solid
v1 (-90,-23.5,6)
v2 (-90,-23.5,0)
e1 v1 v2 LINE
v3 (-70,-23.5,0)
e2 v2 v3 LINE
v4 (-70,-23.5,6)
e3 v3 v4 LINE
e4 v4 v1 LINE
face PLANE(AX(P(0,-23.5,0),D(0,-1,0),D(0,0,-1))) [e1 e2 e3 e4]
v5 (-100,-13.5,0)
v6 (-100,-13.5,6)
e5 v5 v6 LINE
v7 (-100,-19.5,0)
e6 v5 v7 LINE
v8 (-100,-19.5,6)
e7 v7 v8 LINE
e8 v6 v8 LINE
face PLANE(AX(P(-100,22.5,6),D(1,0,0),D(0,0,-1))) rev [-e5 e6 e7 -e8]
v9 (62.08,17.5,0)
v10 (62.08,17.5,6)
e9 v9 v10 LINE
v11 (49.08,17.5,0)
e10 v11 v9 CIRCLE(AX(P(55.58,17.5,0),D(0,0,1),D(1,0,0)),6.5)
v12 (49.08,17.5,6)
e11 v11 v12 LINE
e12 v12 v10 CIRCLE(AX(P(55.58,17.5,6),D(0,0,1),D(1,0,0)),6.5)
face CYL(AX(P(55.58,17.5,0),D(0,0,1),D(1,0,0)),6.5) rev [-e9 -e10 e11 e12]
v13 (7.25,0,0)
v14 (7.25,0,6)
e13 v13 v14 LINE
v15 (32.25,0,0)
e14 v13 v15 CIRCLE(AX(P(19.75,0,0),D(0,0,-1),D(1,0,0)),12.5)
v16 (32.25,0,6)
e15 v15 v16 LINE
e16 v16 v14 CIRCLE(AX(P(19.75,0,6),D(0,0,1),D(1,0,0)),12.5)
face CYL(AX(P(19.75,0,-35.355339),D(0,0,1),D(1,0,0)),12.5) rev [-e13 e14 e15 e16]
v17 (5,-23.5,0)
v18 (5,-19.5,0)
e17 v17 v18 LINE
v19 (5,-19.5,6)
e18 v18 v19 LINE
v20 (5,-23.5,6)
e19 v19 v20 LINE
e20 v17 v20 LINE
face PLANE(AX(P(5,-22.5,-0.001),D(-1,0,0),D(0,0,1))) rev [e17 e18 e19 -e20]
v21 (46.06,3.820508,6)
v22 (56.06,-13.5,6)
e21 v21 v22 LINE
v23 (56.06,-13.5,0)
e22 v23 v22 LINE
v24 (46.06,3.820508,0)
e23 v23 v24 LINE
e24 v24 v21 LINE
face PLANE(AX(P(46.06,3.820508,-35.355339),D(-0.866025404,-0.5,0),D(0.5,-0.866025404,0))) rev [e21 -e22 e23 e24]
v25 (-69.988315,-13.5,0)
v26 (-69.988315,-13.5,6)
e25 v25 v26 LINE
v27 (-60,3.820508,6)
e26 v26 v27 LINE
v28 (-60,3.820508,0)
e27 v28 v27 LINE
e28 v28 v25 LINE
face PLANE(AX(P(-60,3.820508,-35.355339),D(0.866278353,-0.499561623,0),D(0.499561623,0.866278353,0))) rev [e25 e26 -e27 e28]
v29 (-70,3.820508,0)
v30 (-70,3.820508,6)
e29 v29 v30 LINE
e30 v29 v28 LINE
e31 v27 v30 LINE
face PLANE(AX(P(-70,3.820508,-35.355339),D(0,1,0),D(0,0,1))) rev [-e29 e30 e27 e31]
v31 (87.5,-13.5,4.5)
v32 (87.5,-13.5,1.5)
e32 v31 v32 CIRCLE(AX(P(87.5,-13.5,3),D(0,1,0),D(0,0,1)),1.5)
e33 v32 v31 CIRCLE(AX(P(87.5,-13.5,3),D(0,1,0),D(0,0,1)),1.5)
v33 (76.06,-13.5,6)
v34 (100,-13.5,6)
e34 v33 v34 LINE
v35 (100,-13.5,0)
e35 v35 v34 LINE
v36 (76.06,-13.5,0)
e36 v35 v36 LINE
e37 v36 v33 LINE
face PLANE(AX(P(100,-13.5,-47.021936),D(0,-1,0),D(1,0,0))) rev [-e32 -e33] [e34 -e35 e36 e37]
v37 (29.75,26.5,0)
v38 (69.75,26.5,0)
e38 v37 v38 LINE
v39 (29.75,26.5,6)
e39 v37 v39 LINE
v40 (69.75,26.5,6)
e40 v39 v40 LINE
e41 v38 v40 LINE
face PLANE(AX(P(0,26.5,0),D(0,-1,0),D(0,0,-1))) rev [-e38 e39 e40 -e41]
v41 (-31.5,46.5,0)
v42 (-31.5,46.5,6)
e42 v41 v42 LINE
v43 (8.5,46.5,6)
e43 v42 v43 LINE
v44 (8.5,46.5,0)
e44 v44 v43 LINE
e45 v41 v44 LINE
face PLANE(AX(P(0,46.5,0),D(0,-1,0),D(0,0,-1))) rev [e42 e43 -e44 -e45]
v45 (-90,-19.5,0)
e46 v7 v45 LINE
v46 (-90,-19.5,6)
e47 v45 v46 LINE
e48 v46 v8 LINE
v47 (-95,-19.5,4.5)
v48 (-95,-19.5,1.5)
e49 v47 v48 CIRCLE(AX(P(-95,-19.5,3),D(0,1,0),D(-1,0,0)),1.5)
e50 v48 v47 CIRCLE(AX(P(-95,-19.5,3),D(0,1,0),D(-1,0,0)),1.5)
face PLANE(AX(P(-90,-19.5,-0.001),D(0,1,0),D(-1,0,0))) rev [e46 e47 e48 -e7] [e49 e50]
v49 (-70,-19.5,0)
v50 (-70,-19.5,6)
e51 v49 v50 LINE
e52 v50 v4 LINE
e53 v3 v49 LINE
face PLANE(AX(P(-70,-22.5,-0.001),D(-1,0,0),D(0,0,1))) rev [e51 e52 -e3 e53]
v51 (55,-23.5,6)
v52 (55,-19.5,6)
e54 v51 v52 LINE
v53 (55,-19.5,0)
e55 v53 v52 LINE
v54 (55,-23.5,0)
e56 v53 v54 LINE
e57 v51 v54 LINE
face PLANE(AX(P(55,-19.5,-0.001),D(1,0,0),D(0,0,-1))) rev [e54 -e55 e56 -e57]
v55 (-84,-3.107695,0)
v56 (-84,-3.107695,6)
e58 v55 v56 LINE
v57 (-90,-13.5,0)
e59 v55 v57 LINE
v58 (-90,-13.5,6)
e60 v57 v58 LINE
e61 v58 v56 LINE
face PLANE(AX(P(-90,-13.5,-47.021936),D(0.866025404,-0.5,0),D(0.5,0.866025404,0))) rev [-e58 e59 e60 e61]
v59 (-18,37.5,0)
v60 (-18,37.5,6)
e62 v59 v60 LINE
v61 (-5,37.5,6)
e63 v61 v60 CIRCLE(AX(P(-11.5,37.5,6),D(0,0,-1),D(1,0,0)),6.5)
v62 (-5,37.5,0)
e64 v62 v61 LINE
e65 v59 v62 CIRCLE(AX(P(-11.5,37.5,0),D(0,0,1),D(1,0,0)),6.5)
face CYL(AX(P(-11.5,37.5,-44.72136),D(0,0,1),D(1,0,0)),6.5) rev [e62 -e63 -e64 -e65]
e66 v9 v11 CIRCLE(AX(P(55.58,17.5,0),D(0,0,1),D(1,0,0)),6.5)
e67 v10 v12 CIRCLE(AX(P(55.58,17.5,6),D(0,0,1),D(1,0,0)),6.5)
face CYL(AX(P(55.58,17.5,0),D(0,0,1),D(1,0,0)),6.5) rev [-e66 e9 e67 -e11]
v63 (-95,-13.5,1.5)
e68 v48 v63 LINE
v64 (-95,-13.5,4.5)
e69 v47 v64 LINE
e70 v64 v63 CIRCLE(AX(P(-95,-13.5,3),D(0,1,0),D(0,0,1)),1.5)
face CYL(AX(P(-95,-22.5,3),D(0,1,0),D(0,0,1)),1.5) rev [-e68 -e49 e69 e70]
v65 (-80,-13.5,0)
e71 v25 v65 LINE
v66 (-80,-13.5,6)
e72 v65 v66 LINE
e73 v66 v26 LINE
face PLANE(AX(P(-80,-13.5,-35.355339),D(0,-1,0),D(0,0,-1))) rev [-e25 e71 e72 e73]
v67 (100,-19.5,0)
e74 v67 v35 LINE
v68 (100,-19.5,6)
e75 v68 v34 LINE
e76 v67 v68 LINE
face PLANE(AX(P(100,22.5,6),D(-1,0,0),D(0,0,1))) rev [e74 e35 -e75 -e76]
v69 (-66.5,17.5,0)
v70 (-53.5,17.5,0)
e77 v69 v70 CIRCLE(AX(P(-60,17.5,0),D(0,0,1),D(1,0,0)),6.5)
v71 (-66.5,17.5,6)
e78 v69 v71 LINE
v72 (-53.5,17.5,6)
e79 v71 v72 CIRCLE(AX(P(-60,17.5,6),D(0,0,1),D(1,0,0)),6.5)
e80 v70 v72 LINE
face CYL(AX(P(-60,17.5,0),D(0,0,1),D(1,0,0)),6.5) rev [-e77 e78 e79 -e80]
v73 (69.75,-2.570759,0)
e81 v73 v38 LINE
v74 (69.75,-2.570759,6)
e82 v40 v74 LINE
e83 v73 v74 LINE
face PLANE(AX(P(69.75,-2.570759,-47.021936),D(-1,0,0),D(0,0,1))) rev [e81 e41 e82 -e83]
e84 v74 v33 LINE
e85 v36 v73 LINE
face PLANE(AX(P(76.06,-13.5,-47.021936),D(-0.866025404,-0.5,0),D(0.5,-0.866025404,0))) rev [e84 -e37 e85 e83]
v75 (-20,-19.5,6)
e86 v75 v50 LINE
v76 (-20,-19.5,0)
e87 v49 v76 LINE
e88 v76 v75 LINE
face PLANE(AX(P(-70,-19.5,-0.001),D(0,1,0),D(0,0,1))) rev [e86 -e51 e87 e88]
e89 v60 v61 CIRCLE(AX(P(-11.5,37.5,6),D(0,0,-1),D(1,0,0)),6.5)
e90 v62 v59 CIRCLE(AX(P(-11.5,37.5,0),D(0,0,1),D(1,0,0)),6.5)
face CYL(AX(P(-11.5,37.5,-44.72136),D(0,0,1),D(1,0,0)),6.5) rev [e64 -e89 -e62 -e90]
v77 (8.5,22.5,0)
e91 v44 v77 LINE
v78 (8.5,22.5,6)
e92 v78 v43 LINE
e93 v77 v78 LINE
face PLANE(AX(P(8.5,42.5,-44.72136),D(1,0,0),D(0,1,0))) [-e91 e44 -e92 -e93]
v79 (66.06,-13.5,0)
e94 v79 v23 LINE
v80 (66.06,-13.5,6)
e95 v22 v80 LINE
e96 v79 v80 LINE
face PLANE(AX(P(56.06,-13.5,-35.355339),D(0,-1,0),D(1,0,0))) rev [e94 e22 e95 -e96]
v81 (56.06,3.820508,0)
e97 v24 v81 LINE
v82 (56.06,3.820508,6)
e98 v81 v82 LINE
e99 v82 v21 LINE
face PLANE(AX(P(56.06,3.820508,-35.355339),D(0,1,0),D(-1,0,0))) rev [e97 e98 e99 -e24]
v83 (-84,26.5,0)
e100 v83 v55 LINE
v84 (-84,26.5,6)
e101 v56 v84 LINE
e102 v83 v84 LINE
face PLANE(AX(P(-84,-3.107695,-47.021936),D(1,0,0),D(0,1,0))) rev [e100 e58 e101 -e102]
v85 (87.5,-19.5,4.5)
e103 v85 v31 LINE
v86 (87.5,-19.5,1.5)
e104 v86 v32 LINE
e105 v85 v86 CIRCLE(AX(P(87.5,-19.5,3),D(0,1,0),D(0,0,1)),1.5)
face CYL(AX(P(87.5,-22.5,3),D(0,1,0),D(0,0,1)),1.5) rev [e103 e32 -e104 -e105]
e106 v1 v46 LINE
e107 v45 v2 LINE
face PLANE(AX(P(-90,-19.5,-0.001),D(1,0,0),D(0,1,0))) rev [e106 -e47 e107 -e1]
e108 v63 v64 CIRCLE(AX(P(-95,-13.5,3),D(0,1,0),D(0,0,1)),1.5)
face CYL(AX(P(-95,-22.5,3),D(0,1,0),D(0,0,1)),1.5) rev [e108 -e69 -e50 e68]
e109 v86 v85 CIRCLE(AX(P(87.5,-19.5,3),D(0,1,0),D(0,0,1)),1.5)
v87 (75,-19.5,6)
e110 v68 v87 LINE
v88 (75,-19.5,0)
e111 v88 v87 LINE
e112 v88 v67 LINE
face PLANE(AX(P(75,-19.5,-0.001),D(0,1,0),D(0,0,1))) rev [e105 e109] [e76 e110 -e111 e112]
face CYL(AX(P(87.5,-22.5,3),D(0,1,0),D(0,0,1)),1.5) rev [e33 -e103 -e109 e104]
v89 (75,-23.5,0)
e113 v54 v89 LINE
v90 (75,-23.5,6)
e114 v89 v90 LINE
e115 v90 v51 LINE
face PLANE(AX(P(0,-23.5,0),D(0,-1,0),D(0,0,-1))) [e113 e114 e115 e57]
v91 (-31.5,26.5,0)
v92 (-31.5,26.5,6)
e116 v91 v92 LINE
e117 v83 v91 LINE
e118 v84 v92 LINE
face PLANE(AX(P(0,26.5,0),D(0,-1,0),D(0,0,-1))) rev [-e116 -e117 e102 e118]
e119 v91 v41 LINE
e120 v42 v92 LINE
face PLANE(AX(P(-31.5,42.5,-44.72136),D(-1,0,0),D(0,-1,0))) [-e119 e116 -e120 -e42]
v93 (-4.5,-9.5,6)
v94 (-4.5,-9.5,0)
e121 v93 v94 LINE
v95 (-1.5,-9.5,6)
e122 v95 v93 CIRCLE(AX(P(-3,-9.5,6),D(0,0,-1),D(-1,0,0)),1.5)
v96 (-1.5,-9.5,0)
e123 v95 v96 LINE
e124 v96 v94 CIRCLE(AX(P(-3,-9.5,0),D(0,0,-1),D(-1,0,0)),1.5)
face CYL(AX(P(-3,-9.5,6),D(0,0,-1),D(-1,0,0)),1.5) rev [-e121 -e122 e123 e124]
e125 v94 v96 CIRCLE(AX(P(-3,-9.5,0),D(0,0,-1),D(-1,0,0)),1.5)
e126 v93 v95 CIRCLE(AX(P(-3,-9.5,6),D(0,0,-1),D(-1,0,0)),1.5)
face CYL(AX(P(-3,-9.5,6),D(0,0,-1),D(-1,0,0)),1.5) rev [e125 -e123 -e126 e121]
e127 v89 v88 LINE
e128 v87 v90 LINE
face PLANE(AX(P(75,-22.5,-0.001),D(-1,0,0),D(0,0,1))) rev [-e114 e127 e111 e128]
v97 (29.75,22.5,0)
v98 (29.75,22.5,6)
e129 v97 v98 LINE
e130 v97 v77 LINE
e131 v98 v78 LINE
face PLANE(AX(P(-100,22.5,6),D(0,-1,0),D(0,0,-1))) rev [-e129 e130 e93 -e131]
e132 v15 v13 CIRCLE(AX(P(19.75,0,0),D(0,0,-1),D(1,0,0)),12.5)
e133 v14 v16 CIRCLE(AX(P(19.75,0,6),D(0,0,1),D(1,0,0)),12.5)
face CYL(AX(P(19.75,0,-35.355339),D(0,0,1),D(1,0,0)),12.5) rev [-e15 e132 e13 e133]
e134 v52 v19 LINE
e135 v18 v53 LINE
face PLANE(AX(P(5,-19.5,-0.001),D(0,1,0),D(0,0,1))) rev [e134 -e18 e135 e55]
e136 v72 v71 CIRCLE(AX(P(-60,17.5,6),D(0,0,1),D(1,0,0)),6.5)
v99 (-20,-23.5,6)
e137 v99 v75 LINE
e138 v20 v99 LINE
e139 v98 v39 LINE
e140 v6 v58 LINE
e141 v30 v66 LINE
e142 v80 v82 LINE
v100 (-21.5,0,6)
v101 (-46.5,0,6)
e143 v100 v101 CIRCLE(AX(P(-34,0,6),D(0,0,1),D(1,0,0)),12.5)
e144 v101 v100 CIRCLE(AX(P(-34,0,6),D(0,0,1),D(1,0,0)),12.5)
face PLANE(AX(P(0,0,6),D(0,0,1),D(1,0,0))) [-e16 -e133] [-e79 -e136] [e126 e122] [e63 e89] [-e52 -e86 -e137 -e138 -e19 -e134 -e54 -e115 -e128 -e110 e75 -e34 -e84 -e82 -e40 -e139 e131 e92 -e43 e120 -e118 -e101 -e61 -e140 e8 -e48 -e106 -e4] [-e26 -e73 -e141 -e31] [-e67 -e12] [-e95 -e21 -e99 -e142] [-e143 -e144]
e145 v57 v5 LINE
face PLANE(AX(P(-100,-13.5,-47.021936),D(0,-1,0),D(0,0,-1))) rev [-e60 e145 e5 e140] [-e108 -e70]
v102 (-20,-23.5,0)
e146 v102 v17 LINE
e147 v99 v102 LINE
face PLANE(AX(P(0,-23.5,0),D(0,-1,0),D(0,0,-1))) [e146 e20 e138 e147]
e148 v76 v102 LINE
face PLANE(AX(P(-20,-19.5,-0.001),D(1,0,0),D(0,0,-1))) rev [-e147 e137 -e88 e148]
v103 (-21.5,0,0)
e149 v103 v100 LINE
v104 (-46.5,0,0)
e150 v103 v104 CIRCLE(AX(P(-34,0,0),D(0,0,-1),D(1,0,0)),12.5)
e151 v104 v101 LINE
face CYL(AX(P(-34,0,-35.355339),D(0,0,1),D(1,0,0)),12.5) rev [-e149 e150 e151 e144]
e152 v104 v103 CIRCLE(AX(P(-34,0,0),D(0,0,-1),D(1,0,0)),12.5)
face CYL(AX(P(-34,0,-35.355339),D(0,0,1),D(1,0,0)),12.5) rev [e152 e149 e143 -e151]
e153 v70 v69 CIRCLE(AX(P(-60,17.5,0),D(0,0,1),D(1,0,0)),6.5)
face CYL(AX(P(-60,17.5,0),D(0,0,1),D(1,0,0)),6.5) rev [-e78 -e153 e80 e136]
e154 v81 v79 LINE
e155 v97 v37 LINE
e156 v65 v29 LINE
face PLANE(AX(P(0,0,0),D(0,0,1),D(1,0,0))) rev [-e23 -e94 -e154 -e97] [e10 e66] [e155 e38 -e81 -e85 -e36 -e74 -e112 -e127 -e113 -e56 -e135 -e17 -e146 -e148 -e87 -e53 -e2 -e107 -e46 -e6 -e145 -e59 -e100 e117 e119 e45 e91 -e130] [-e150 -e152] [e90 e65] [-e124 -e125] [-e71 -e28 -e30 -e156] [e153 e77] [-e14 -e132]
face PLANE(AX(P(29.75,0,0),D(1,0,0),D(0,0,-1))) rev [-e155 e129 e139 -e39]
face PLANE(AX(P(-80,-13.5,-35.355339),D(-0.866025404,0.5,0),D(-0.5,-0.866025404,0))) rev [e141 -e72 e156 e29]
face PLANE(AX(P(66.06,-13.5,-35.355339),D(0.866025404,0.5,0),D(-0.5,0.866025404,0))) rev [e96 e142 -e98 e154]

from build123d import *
from build123d.topology import SkipClean

# Parameters (mm, degrees)
SKETCH1_W           = 200
SKETCH1_H           = 45
BOSS_EXTRUDE1_DEPTH = 6
CUT_EXTRUDE1_REACH  = 104.675
SKETCH2_W           = 10
SKETCH2_H           = 3
SKETCH2_W_2         = 50
SKETCH2_W_3         = 25
BOSS_EXTRUDE2_DEPTH = 6
CUT_EXTRUDE2_DEPTH  = 6
CUT_EXTRUDE3_DEPTH  = 6
SKETCH15_R          = 12.5
CUT_EXTRUDE4_DEPTH  = 6
BOSS_EXTRUDE3_DEPTH = 6
SKETCH20_R          = 1.5
CUT_EXTRUDE5_DEPTH  = 111.44568801
SKETCH21_R          = 1.5
CUT_EXTRUDE6_DEPTH  = 117.773284616
SKETCH24_W          = 20
SKETCH24_H          = 6
SKETCH24_W_2        = 25
BOSS_EXTRUDE4_DEPTH = 1
SKETCH25_R          = 6.5
BOSS_EXTRUDE5_DEPTH = 6
SKETCH26_R          = 6.5
CUT_EXTRUDE7_DEPTH  = 111.44568801


with BuildPart() as part:
    # Sketch1 → Boss-Extrude1 (new body)
    with BuildSketch(Plane.XY):
        Rectangle(SKETCH1_W, SKETCH1_H)
    extrude(amount=BOSS_EXTRUDE1_DEPTH)

    # Sketch2 → Cut-Extrude1 (cut, up to next)
    with BuildSketch(Plane.XY.offset(6), mode=Mode.PRIVATE) as cut_extrude1_sk1:
        with Locations((-95, -21)):
            Rectangle(SKETCH2_W, SKETCH2_H)
    cut_extrude1_tool1 = extrude(cut_extrude1_sk1.sketch, amount=-CUT_EXTRUDE1_REACH, mode=Mode.PRIVATE) & part.part
    # Sketch2 → Cut-Extrude1 (cut, up to next)
    with BuildSketch(Plane.XY.offset(6), mode=Mode.PRIVATE) as cut_extrude1_sk2:
        with Locations((-45, -21)):
            Rectangle(SKETCH2_W_2, SKETCH2_H)
    cut_extrude1_tool2 = extrude(cut_extrude1_sk2.sketch, amount=-CUT_EXTRUDE1_REACH, mode=Mode.PRIVATE) & part.part
    # Sketch2 → Cut-Extrude1 (cut, up to next)
    with BuildSketch(Plane.XY.offset(6), mode=Mode.PRIVATE) as cut_extrude1_sk3:
        with Locations((30, -21)):
            Rectangle(SKETCH2_W_2, SKETCH2_H)
    cut_extrude1_tool3 = extrude(cut_extrude1_sk3.sketch, amount=-CUT_EXTRUDE1_REACH, mode=Mode.PRIVATE) & part.part
    # Sketch2 → Cut-Extrude1 (cut, up to next)
    with BuildSketch(Plane.XY.offset(6), mode=Mode.PRIVATE) as cut_extrude1_sk4:
        with Locations((87.5, -21)):
            Rectangle(SKETCH2_W_3, SKETCH2_H)
    cut_extrude1_tool4 = extrude(cut_extrude1_sk4.sketch, amount=-CUT_EXTRUDE1_REACH, mode=Mode.PRIVATE) & part.part
    add(cut_extrude1_tool1.solids().sort_by_distance((-95, -21, 6))[0], mode=Mode.SUBTRACT)
    add(cut_extrude1_tool2.solids().sort_by_distance((-45, -21, 6))[0], mode=Mode.SUBTRACT)
    add(cut_extrude1_tool3.solids().sort_by_distance((30, -21, 6))[0], mode=Mode.SUBTRACT)
    add(cut_extrude1_tool4.solids().sort_by_distance((87.5, -21, 6))[0], mode=Mode.SUBTRACT)

    # Sketch3 → Boss-Extrude2 (add)
    with BuildSketch(Plane.XY.offset(6)):
        with BuildLine():
            Line((-31.5, 42.5), (-31.5, 22.5))
            Line((-31.5, 22.5), (8.5, 22.5))
            Line((8.5, 22.5), (8.5, 42.5))
            Line((8.5, 42.5), (-2, 42.5))
            Line((-2, 42.5), (-2, 37.5))
            Line((-2, 37.5), (-5, 37.5))
            ThreePointArc((-5, 37.5), (-11.5, 31), (-18, 37.5))
            Line((-18, 37.5), (-21, 37.5))
            Line((-21, 37.5), (-21, 42.5))
            Line((-21, 42.5), (-31.5, 42.5))
        make_face()
    extrude(amount=-BOSS_EXTRUDE2_DEPTH)

    # Sketch4 → Cut-Extrude2 (cut)
    with BuildSketch(Plane.XY.offset(6)):
        with BuildLine():
            Line((-53.5, 17.5), (-50.5, 17.5))
            Line((-50.5, 17.5), (-50.5, 22.5))
            Line((-50.5, 22.5), (-69.5, 22.5))
            Line((-69.5, 22.5), (-69.5, 17.5))
            Line((-69.5, 17.5), (-66.5, 17.5))
            ThreePointArc((-66.5, 17.5), (-60, 11), (-53.5, 17.5))
        make_face()
        with BuildLine():
            Line((53, 17.5), (56, 17.5))
            Line((56, 17.5), (56, 22.5))
            Line((56, 22.5), (37, 22.5))
            Line((37, 22.5), (37, 17.5))
            Line((37, 17.5), (40, 17.5))
            ThreePointArc((40, 17.5), (46.5, 11), (53, 17.5))
        make_face()
    extrude(amount=-CUT_EXTRUDE2_DEPTH, mode=Mode.SUBTRACT)

    # Sketch11 → Cut-Extrude3 (cut)
    with BuildSketch(Plane.XY.offset(6)):
        Polygon((-100, -13.5), (-90, -13.5), (-84, -3.107695155), (-84, 22.5), (-100, 22.5), align=None)
        Polygon((100, -13.5), (76.06, -13.5), (69.75, -2.570759404), (69.75, 22.5), (100, 22.5), align=None)
    extrude(amount=-CUT_EXTRUDE3_DEPTH, mode=Mode.SUBTRACT)

    # Sketch15 → Cut-Extrude4 (cut)
    with BuildSketch(Plane.XY.offset(6)):
        with Locations((-34, 0)):
            Circle(SKETCH15_R)
        with Locations((19.75, 0)):
            Circle(SKETCH15_R)
        Polygon((-80, -13.5), (-70, 3.820508076), (-60, 3.820508076), (-69.988315066, -13.5), align=None)
        Polygon((66.06, -13.5), (56.06, 3.820508076), (46.06, 3.820508076), (56.06, -13.5), align=None)
    extrude(amount=-CUT_EXTRUDE4_DEPTH, mode=Mode.SUBTRACT)

    # Sketch19 → Boss-Extrude3 (add)
    with SkipClean():  # the faces are left unmerged after this step: merging them gives an invalid solid
        with BuildSketch(Plane.XY.offset(6)):
            with BuildLine():
                Line((-84, 26.5), (-84, 22.5))
                Line((-84, 22.5), (-69.5, 22.5))
                Line((-69.5, 22.5), (-69.5, 17.5))
                Line((-69.5, 17.5), (-66.5, 17.5))
                ThreePointArc((-66.5, 17.5), (-60, 24), (-53.5, 17.5))
                Line((-53.5, 17.5), (-50.5, 17.5))
                Line((-50.5, 17.5), (-50.5, 22.5))
                Line((-50.5, 22.5), (-31.5, 22.5))
                Line((-31.5, 22.5), (-31.5, 26.5))
                Line((-31.5, 26.5), (-84, 26.5))
            make_face()
            with BuildLine():
                Line((-31.5, 46.5), (-31.5, 42.5))
                Line((-31.5, 42.5), (-21, 42.5))
                Line((-21, 42.5), (-21, 37.5))
                Line((-21, 37.5), (-18, 37.5))
                ThreePointArc((-18, 37.5), (-11.5, 44), (-5, 37.5))
                Line((-5, 37.5), (-2, 37.5))
                Line((-2, 37.5), (-2, 42.5))
                Line((-2, 42.5), (8.5, 42.5))
                Line((8.5, 42.5), (8.5, 46.5))
                Line((8.5, 46.5), (-31.5, 46.5))
            make_face()
            with BuildLine():
                Line((29.75, 26.5), (29.75, 22.5))
                Line((29.75, 22.5), (37, 22.5))
                Line((37, 22.5), (37, 17.5))
                Line((37, 17.5), (40, 17.5))
                ThreePointArc((40, 17.5), (46.5, 24), (53, 17.5))
                Line((53, 17.5), (56, 17.5))
                Line((56, 17.5), (56, 22.5))
                Line((56, 22.5), (69.75, 22.5))
                Line((69.75, 22.5), (69.75, 26.5))
                Line((69.75, 26.5), (29.75, 26.5))
            make_face()
        extrude(amount=-BOSS_EXTRUDE3_DEPTH)

    # Sketch20 → Cut-Extrude5 (cut, through all)
    with SkipClean():  # the faces are left unmerged after this step: merging them gives an invalid solid
        with BuildSketch(Plane(origin=(0, 0, 0), x_dir=(-1, 0, 0), z_dir=(0, 0, -1))):
            with Locations((3, -9.5)):
                Circle(SKETCH20_R)
        extrude(amount=-CUT_EXTRUDE5_DEPTH, mode=Mode.SUBTRACT)

    # Sketch21 → Cut-Extrude6 (cut, through all)
    with SkipClean():  # the faces are left unmerged after this step: merging them gives an invalid solid
        with BuildSketch(Plane(origin=(0, -13.5, 0), x_dir=(1, 0, 0), z_dir=(0, 1, 0))):
            with Locations(Location((87.5, -3, 0), (0, 0, 270))):
                Circle(SKETCH21_R)
            with Locations(Location((-95, -3, 0), (0, 0, 270))):
                Circle(SKETCH21_R)
        extrude(amount=-CUT_EXTRUDE6_DEPTH, mode=Mode.SUBTRACT)

    # Sketch24 → Boss-Extrude4 (add)
    with SkipClean():  # the faces are left unmerged after this step: merging them gives an invalid solid
        with BuildSketch(Plane.XZ.offset(22.5)):
            with Locations((-80, 3)):
                Rectangle(SKETCH24_W, SKETCH24_H)
            with Locations((-7.5, 3)):
                Rectangle(SKETCH24_W_2, SKETCH24_H)
            with Locations((65, 3)):
                Rectangle(SKETCH24_W, SKETCH24_H)
        extrude(amount=BOSS_EXTRUDE4_DEPTH)

    # Sketch25 → Boss-Extrude5 (add)
    with BuildSketch(Plane.XY.offset(6)):
        with Locations((46.5, 17.5)):
            Circle(SKETCH25_R)
        with Locations((-60, 17.5)):
            Circle(SKETCH25_R)
    extrude(amount=-BOSS_EXTRUDE5_DEPTH)

    # Sketch26 → Cut-Extrude7 (cut, through all)
    with BuildSketch(Plane.XY.offset(6)):
        with Locations((55.58, 17.5)):
            Circle(SKETCH26_R)
        with Locations((-60, 17.5)):
            Circle(SKETCH26_R)
    extrude(amount=-CUT_EXTRUDE7_DEPTH, mode=Mode.SUBTRACT)


solid = part.part
